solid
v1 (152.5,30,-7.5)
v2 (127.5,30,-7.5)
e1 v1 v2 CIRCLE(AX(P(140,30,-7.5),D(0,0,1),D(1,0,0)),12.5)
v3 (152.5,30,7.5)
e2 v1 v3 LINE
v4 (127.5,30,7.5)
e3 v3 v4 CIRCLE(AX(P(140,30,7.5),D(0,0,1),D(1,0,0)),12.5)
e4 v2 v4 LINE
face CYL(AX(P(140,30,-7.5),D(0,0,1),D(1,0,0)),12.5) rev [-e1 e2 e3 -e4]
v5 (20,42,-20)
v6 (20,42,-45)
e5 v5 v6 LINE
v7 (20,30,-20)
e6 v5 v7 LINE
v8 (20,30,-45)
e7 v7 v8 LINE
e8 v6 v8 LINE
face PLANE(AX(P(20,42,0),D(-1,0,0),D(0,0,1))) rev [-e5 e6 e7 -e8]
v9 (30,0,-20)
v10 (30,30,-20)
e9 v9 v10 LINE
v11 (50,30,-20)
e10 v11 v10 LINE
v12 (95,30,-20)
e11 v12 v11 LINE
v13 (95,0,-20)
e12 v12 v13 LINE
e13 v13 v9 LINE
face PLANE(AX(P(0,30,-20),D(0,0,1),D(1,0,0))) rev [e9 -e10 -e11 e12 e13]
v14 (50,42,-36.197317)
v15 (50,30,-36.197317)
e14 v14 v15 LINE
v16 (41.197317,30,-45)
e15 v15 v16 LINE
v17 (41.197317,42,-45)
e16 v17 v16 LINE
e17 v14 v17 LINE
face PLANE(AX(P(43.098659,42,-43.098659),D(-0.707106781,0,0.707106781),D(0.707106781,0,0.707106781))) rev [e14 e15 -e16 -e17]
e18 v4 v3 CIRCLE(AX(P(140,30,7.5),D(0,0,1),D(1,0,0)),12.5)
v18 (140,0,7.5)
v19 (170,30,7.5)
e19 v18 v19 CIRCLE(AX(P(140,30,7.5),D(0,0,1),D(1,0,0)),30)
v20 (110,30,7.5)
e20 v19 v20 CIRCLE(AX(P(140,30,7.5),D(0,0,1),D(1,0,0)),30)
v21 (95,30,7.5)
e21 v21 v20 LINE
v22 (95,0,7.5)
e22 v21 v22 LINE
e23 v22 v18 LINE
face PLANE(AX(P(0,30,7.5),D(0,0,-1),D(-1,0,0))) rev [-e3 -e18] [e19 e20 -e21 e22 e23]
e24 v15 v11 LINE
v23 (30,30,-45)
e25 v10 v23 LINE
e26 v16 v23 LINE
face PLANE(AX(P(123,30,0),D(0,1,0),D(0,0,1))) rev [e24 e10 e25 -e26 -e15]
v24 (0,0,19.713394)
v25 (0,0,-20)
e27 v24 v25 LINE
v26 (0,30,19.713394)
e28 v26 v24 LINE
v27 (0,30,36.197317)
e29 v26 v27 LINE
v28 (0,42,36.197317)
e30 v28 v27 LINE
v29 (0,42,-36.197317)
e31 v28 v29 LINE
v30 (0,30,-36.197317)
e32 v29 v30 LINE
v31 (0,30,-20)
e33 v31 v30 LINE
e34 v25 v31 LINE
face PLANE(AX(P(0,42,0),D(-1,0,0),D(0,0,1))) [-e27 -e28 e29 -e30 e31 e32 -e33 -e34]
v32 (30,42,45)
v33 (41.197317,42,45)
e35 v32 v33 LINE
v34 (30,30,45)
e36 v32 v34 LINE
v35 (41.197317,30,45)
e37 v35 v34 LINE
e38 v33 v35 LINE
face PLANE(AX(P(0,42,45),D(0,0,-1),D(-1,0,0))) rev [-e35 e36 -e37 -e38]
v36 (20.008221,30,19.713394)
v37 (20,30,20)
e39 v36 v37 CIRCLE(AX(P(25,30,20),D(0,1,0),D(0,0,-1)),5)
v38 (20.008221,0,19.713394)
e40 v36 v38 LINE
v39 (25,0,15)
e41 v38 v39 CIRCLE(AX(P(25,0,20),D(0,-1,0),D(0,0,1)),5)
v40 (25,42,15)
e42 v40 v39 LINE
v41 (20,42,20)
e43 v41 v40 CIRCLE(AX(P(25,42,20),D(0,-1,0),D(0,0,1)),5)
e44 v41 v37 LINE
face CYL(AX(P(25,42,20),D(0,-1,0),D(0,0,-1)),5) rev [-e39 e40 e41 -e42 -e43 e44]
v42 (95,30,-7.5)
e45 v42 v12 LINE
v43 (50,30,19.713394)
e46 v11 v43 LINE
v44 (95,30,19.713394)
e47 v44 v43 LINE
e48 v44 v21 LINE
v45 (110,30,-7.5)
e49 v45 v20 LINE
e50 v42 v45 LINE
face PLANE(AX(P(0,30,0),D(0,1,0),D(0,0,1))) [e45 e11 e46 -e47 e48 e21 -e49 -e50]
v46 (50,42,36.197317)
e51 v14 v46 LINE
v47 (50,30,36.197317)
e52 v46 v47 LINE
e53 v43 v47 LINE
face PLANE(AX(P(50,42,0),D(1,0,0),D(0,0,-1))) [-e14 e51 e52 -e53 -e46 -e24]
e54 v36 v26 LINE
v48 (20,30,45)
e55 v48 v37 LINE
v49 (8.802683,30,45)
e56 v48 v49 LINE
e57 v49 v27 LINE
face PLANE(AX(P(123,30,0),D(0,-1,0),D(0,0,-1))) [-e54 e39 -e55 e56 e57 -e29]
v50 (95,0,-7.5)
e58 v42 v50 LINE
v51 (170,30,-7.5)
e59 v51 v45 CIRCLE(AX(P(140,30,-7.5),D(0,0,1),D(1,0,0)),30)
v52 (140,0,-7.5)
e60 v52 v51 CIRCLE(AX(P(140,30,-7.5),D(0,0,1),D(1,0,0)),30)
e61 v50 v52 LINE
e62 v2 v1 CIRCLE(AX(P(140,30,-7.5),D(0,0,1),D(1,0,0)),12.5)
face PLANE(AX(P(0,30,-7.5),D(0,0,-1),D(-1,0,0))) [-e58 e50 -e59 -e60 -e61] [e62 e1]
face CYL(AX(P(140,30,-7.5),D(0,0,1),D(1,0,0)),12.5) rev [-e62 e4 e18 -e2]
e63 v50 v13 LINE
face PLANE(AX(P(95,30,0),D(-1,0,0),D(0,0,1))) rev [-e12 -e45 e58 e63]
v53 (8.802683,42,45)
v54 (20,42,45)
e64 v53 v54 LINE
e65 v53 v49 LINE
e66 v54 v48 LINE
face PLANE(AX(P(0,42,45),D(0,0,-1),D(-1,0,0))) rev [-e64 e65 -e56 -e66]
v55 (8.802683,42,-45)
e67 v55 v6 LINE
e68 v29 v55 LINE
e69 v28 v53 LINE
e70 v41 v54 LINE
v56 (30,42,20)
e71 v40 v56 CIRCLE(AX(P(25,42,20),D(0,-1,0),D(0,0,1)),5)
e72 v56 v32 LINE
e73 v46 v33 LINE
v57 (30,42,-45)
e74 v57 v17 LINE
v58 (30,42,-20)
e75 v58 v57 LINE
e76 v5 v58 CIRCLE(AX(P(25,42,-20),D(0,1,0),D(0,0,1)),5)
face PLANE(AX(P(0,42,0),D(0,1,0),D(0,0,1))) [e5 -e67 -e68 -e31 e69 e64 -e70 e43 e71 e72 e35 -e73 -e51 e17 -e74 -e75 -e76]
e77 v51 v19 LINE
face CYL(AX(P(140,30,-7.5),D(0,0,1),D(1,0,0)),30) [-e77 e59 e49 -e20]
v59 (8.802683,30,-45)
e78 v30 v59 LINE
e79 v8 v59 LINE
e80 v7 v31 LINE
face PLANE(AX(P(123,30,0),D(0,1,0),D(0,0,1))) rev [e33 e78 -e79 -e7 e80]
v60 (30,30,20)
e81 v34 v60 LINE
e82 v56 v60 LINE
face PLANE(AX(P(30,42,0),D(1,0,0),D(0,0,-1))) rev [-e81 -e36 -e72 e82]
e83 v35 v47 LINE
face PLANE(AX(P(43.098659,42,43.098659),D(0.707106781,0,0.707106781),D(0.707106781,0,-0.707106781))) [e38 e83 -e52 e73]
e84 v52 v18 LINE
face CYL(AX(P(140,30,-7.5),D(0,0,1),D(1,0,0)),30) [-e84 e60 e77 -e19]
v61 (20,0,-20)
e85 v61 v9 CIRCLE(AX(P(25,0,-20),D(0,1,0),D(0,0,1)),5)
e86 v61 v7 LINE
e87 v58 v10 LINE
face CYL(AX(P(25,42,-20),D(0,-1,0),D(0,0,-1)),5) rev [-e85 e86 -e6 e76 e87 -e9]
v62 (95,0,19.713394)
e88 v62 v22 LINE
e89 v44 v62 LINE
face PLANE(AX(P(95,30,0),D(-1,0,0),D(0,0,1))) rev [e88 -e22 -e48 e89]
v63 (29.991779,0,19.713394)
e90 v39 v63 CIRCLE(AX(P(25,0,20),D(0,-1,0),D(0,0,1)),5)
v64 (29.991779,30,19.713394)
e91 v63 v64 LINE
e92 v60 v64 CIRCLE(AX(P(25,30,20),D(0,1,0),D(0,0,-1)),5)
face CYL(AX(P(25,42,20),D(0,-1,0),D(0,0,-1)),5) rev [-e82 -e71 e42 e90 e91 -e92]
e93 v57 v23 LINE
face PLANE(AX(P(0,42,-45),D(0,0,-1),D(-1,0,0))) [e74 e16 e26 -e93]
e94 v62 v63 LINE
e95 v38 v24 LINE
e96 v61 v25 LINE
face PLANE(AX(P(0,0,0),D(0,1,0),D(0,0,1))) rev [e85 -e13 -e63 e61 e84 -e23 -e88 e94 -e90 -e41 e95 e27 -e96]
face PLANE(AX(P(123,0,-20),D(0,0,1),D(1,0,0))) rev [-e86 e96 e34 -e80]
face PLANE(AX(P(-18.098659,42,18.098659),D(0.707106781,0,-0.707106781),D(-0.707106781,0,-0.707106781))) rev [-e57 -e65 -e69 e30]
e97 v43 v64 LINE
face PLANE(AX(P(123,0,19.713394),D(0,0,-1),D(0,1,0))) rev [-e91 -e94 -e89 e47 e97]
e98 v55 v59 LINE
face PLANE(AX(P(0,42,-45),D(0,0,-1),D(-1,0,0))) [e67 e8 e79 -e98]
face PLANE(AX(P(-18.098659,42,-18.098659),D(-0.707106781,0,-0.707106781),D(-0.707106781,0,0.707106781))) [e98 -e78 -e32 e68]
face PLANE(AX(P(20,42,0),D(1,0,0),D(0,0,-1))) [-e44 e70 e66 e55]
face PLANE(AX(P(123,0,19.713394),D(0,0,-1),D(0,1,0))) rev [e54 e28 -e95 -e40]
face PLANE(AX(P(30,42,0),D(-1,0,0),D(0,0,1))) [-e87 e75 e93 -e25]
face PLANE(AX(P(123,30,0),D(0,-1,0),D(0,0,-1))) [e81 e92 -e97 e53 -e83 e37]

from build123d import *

# Parameters (mm, degrees)
BASE_BODY_42MM_DEPTH = 42
SKETCH1_5_W          = 15
SKETCH1_5_H          = 15
SIDE_BOSS_30MM_DEPTH = 30
SLOTS_SKETCH_W       = 16.483923251
SLOTS_SKETCH_H       = 30
SLOTS_SKETCH_W_2     = 8.802682669
SLOTS_SKETCH_W_3     = 16.197317331
SLOTS_CUT_DEPTH      = 123
SKETCH1_6_W          = 30
SKETCH1_6_H          = 15
EYE_BOSS_70MM_DEPTH  = 70
WEB_SKETCH_W         = 30
WEB_SKETCH_H         = 15
WEB_BOSS_70MM_DEPTH  = 70
PIN_BORE_SKETCH_R    = 12.5
PIN_BORE_CUT_DEPTH   = 15


with BuildPart() as part:
    # Link Profile Sketch → Base Body 42mm (new body)
    with BuildSketch(Plane(origin=(0, 0, 0), x_dir=(1, 0, 0), z_dir=(0, 1, 0))):
        with BuildLine():
            Line((20, -20), (20, -45))
            Line((20, -45), (8.802682669, -45))
            Line((8.802682669, -45), (0, -36.197317331))
            Line((0, -36.197317331), (0, 0))
            Line((0, 0), (0, 36.197317331))
            Line((0, 36.197317331), (8.802682669, 45))
            Line((8.802682669, 45), (20, 45))
            Line((20, 45), (20, 20))
            ThreePointArc((20, 20), (25, 15), (30, 20))
            Line((30, 20), (30, 45))
            Line((30, 45), (41.197317331, 45))
            Line((41.197317331, 45), (50, 36.197317331))
            Line((50, 36.197317331), (50, -36.197317331))
            Line((50, -36.197317331), (41.197317331, -45))
            Line((41.197317331, -45), (30, -45))
            Line((30, -45), (30, -20))
            ThreePointArc((30, -20), (25, -15), (20, -20))
        make_face()
    extrude(amount=BASE_BODY_42MM_DEPTH)

    # Sketch1_5 → Side Boss 30mm (add)
    with BuildSketch(Plane(origin=(0, 0, 0), x_dir=(1, 0, 0), z_dir=(0, 1, 0))):
        Polygon((95, 20), (50, 20), (50, -20), (95, -20), (95, -7.5), (95, 7.5), align=None)
        with Locations((102.5, 0)):
            Rectangle(SKETCH1_5_W, SKETCH1_5_H)
    extrude(amount=SIDE_BOSS_30MM_DEPTH)

    # Slots Sketch → Slots Cut (cut)
    with BuildSketch(Plane.ZY):
        with Locations((27.955355706, 15)):
            Rectangle(SLOTS_SKETCH_W, SLOTS_SKETCH_H)
        with Locations((40.598658665, 15)):
            Rectangle(SLOTS_SKETCH_W_2, SLOTS_SKETCH_H)
        with Locations((-28.098658666, 15)):
            Rectangle(SLOTS_SKETCH_W_3, SLOTS_SKETCH_H)
        with Locations((-40.598658665, 15)):
            Rectangle(SLOTS_SKETCH_W_2, SLOTS_SKETCH_H)
    extrude(amount=-SLOTS_CUT_DEPTH, mode=Mode.SUBTRACT)

    # Sketch1_6 → Eye Boss 70mm (add)
    with BuildSketch(Plane(origin=(0, 0, 0), x_dir=(1, 0, 0), z_dir=(0, 1, 0))):
        with Locations((125, 0)):
            Rectangle(SKETCH1_6_W, SKETCH1_6_H)
    extrude(amount=EYE_BOSS_70MM_DEPTH)

    # Web Sketch → Web Boss 70mm (add)
    with BuildSketch(Plane(origin=(0, 70, 0), x_dir=(1, 0, 0), z_dir=(0, 1, 0))):
        with Locations((155, 0)):
            Rectangle(WEB_SKETCH_W, WEB_SKETCH_H)
    extrude(amount=-WEB_BOSS_70MM_DEPTH)

    # Pin Bore Sketch → Pin Bore Cut (cut)
    with BuildSketch(Plane.XY.offset(7.5)):
        with Locations((140, 30)):
            Circle(PIN_BORE_SKETCH_R)
        with BuildLine():
            Line((110, 70), (110, 30))
            ThreePointArc((110, 30), (140, 60), (170, 30))
            Line((170, 30), (170, 70))
            Line((170, 70), (110, 70))
        make_face()
        with BuildLine():
            Line((170, 0), (170, 30))
            ThreePointArc((170, 30), (161.213203436, 8.786796564), (140, 0))
            Line((140, 0), (170, 0))
        make_face()
    extrude(amount=-PIN_BORE_CUT_DEPTH, mode=Mode.SUBTRACT)


solid = part.part
